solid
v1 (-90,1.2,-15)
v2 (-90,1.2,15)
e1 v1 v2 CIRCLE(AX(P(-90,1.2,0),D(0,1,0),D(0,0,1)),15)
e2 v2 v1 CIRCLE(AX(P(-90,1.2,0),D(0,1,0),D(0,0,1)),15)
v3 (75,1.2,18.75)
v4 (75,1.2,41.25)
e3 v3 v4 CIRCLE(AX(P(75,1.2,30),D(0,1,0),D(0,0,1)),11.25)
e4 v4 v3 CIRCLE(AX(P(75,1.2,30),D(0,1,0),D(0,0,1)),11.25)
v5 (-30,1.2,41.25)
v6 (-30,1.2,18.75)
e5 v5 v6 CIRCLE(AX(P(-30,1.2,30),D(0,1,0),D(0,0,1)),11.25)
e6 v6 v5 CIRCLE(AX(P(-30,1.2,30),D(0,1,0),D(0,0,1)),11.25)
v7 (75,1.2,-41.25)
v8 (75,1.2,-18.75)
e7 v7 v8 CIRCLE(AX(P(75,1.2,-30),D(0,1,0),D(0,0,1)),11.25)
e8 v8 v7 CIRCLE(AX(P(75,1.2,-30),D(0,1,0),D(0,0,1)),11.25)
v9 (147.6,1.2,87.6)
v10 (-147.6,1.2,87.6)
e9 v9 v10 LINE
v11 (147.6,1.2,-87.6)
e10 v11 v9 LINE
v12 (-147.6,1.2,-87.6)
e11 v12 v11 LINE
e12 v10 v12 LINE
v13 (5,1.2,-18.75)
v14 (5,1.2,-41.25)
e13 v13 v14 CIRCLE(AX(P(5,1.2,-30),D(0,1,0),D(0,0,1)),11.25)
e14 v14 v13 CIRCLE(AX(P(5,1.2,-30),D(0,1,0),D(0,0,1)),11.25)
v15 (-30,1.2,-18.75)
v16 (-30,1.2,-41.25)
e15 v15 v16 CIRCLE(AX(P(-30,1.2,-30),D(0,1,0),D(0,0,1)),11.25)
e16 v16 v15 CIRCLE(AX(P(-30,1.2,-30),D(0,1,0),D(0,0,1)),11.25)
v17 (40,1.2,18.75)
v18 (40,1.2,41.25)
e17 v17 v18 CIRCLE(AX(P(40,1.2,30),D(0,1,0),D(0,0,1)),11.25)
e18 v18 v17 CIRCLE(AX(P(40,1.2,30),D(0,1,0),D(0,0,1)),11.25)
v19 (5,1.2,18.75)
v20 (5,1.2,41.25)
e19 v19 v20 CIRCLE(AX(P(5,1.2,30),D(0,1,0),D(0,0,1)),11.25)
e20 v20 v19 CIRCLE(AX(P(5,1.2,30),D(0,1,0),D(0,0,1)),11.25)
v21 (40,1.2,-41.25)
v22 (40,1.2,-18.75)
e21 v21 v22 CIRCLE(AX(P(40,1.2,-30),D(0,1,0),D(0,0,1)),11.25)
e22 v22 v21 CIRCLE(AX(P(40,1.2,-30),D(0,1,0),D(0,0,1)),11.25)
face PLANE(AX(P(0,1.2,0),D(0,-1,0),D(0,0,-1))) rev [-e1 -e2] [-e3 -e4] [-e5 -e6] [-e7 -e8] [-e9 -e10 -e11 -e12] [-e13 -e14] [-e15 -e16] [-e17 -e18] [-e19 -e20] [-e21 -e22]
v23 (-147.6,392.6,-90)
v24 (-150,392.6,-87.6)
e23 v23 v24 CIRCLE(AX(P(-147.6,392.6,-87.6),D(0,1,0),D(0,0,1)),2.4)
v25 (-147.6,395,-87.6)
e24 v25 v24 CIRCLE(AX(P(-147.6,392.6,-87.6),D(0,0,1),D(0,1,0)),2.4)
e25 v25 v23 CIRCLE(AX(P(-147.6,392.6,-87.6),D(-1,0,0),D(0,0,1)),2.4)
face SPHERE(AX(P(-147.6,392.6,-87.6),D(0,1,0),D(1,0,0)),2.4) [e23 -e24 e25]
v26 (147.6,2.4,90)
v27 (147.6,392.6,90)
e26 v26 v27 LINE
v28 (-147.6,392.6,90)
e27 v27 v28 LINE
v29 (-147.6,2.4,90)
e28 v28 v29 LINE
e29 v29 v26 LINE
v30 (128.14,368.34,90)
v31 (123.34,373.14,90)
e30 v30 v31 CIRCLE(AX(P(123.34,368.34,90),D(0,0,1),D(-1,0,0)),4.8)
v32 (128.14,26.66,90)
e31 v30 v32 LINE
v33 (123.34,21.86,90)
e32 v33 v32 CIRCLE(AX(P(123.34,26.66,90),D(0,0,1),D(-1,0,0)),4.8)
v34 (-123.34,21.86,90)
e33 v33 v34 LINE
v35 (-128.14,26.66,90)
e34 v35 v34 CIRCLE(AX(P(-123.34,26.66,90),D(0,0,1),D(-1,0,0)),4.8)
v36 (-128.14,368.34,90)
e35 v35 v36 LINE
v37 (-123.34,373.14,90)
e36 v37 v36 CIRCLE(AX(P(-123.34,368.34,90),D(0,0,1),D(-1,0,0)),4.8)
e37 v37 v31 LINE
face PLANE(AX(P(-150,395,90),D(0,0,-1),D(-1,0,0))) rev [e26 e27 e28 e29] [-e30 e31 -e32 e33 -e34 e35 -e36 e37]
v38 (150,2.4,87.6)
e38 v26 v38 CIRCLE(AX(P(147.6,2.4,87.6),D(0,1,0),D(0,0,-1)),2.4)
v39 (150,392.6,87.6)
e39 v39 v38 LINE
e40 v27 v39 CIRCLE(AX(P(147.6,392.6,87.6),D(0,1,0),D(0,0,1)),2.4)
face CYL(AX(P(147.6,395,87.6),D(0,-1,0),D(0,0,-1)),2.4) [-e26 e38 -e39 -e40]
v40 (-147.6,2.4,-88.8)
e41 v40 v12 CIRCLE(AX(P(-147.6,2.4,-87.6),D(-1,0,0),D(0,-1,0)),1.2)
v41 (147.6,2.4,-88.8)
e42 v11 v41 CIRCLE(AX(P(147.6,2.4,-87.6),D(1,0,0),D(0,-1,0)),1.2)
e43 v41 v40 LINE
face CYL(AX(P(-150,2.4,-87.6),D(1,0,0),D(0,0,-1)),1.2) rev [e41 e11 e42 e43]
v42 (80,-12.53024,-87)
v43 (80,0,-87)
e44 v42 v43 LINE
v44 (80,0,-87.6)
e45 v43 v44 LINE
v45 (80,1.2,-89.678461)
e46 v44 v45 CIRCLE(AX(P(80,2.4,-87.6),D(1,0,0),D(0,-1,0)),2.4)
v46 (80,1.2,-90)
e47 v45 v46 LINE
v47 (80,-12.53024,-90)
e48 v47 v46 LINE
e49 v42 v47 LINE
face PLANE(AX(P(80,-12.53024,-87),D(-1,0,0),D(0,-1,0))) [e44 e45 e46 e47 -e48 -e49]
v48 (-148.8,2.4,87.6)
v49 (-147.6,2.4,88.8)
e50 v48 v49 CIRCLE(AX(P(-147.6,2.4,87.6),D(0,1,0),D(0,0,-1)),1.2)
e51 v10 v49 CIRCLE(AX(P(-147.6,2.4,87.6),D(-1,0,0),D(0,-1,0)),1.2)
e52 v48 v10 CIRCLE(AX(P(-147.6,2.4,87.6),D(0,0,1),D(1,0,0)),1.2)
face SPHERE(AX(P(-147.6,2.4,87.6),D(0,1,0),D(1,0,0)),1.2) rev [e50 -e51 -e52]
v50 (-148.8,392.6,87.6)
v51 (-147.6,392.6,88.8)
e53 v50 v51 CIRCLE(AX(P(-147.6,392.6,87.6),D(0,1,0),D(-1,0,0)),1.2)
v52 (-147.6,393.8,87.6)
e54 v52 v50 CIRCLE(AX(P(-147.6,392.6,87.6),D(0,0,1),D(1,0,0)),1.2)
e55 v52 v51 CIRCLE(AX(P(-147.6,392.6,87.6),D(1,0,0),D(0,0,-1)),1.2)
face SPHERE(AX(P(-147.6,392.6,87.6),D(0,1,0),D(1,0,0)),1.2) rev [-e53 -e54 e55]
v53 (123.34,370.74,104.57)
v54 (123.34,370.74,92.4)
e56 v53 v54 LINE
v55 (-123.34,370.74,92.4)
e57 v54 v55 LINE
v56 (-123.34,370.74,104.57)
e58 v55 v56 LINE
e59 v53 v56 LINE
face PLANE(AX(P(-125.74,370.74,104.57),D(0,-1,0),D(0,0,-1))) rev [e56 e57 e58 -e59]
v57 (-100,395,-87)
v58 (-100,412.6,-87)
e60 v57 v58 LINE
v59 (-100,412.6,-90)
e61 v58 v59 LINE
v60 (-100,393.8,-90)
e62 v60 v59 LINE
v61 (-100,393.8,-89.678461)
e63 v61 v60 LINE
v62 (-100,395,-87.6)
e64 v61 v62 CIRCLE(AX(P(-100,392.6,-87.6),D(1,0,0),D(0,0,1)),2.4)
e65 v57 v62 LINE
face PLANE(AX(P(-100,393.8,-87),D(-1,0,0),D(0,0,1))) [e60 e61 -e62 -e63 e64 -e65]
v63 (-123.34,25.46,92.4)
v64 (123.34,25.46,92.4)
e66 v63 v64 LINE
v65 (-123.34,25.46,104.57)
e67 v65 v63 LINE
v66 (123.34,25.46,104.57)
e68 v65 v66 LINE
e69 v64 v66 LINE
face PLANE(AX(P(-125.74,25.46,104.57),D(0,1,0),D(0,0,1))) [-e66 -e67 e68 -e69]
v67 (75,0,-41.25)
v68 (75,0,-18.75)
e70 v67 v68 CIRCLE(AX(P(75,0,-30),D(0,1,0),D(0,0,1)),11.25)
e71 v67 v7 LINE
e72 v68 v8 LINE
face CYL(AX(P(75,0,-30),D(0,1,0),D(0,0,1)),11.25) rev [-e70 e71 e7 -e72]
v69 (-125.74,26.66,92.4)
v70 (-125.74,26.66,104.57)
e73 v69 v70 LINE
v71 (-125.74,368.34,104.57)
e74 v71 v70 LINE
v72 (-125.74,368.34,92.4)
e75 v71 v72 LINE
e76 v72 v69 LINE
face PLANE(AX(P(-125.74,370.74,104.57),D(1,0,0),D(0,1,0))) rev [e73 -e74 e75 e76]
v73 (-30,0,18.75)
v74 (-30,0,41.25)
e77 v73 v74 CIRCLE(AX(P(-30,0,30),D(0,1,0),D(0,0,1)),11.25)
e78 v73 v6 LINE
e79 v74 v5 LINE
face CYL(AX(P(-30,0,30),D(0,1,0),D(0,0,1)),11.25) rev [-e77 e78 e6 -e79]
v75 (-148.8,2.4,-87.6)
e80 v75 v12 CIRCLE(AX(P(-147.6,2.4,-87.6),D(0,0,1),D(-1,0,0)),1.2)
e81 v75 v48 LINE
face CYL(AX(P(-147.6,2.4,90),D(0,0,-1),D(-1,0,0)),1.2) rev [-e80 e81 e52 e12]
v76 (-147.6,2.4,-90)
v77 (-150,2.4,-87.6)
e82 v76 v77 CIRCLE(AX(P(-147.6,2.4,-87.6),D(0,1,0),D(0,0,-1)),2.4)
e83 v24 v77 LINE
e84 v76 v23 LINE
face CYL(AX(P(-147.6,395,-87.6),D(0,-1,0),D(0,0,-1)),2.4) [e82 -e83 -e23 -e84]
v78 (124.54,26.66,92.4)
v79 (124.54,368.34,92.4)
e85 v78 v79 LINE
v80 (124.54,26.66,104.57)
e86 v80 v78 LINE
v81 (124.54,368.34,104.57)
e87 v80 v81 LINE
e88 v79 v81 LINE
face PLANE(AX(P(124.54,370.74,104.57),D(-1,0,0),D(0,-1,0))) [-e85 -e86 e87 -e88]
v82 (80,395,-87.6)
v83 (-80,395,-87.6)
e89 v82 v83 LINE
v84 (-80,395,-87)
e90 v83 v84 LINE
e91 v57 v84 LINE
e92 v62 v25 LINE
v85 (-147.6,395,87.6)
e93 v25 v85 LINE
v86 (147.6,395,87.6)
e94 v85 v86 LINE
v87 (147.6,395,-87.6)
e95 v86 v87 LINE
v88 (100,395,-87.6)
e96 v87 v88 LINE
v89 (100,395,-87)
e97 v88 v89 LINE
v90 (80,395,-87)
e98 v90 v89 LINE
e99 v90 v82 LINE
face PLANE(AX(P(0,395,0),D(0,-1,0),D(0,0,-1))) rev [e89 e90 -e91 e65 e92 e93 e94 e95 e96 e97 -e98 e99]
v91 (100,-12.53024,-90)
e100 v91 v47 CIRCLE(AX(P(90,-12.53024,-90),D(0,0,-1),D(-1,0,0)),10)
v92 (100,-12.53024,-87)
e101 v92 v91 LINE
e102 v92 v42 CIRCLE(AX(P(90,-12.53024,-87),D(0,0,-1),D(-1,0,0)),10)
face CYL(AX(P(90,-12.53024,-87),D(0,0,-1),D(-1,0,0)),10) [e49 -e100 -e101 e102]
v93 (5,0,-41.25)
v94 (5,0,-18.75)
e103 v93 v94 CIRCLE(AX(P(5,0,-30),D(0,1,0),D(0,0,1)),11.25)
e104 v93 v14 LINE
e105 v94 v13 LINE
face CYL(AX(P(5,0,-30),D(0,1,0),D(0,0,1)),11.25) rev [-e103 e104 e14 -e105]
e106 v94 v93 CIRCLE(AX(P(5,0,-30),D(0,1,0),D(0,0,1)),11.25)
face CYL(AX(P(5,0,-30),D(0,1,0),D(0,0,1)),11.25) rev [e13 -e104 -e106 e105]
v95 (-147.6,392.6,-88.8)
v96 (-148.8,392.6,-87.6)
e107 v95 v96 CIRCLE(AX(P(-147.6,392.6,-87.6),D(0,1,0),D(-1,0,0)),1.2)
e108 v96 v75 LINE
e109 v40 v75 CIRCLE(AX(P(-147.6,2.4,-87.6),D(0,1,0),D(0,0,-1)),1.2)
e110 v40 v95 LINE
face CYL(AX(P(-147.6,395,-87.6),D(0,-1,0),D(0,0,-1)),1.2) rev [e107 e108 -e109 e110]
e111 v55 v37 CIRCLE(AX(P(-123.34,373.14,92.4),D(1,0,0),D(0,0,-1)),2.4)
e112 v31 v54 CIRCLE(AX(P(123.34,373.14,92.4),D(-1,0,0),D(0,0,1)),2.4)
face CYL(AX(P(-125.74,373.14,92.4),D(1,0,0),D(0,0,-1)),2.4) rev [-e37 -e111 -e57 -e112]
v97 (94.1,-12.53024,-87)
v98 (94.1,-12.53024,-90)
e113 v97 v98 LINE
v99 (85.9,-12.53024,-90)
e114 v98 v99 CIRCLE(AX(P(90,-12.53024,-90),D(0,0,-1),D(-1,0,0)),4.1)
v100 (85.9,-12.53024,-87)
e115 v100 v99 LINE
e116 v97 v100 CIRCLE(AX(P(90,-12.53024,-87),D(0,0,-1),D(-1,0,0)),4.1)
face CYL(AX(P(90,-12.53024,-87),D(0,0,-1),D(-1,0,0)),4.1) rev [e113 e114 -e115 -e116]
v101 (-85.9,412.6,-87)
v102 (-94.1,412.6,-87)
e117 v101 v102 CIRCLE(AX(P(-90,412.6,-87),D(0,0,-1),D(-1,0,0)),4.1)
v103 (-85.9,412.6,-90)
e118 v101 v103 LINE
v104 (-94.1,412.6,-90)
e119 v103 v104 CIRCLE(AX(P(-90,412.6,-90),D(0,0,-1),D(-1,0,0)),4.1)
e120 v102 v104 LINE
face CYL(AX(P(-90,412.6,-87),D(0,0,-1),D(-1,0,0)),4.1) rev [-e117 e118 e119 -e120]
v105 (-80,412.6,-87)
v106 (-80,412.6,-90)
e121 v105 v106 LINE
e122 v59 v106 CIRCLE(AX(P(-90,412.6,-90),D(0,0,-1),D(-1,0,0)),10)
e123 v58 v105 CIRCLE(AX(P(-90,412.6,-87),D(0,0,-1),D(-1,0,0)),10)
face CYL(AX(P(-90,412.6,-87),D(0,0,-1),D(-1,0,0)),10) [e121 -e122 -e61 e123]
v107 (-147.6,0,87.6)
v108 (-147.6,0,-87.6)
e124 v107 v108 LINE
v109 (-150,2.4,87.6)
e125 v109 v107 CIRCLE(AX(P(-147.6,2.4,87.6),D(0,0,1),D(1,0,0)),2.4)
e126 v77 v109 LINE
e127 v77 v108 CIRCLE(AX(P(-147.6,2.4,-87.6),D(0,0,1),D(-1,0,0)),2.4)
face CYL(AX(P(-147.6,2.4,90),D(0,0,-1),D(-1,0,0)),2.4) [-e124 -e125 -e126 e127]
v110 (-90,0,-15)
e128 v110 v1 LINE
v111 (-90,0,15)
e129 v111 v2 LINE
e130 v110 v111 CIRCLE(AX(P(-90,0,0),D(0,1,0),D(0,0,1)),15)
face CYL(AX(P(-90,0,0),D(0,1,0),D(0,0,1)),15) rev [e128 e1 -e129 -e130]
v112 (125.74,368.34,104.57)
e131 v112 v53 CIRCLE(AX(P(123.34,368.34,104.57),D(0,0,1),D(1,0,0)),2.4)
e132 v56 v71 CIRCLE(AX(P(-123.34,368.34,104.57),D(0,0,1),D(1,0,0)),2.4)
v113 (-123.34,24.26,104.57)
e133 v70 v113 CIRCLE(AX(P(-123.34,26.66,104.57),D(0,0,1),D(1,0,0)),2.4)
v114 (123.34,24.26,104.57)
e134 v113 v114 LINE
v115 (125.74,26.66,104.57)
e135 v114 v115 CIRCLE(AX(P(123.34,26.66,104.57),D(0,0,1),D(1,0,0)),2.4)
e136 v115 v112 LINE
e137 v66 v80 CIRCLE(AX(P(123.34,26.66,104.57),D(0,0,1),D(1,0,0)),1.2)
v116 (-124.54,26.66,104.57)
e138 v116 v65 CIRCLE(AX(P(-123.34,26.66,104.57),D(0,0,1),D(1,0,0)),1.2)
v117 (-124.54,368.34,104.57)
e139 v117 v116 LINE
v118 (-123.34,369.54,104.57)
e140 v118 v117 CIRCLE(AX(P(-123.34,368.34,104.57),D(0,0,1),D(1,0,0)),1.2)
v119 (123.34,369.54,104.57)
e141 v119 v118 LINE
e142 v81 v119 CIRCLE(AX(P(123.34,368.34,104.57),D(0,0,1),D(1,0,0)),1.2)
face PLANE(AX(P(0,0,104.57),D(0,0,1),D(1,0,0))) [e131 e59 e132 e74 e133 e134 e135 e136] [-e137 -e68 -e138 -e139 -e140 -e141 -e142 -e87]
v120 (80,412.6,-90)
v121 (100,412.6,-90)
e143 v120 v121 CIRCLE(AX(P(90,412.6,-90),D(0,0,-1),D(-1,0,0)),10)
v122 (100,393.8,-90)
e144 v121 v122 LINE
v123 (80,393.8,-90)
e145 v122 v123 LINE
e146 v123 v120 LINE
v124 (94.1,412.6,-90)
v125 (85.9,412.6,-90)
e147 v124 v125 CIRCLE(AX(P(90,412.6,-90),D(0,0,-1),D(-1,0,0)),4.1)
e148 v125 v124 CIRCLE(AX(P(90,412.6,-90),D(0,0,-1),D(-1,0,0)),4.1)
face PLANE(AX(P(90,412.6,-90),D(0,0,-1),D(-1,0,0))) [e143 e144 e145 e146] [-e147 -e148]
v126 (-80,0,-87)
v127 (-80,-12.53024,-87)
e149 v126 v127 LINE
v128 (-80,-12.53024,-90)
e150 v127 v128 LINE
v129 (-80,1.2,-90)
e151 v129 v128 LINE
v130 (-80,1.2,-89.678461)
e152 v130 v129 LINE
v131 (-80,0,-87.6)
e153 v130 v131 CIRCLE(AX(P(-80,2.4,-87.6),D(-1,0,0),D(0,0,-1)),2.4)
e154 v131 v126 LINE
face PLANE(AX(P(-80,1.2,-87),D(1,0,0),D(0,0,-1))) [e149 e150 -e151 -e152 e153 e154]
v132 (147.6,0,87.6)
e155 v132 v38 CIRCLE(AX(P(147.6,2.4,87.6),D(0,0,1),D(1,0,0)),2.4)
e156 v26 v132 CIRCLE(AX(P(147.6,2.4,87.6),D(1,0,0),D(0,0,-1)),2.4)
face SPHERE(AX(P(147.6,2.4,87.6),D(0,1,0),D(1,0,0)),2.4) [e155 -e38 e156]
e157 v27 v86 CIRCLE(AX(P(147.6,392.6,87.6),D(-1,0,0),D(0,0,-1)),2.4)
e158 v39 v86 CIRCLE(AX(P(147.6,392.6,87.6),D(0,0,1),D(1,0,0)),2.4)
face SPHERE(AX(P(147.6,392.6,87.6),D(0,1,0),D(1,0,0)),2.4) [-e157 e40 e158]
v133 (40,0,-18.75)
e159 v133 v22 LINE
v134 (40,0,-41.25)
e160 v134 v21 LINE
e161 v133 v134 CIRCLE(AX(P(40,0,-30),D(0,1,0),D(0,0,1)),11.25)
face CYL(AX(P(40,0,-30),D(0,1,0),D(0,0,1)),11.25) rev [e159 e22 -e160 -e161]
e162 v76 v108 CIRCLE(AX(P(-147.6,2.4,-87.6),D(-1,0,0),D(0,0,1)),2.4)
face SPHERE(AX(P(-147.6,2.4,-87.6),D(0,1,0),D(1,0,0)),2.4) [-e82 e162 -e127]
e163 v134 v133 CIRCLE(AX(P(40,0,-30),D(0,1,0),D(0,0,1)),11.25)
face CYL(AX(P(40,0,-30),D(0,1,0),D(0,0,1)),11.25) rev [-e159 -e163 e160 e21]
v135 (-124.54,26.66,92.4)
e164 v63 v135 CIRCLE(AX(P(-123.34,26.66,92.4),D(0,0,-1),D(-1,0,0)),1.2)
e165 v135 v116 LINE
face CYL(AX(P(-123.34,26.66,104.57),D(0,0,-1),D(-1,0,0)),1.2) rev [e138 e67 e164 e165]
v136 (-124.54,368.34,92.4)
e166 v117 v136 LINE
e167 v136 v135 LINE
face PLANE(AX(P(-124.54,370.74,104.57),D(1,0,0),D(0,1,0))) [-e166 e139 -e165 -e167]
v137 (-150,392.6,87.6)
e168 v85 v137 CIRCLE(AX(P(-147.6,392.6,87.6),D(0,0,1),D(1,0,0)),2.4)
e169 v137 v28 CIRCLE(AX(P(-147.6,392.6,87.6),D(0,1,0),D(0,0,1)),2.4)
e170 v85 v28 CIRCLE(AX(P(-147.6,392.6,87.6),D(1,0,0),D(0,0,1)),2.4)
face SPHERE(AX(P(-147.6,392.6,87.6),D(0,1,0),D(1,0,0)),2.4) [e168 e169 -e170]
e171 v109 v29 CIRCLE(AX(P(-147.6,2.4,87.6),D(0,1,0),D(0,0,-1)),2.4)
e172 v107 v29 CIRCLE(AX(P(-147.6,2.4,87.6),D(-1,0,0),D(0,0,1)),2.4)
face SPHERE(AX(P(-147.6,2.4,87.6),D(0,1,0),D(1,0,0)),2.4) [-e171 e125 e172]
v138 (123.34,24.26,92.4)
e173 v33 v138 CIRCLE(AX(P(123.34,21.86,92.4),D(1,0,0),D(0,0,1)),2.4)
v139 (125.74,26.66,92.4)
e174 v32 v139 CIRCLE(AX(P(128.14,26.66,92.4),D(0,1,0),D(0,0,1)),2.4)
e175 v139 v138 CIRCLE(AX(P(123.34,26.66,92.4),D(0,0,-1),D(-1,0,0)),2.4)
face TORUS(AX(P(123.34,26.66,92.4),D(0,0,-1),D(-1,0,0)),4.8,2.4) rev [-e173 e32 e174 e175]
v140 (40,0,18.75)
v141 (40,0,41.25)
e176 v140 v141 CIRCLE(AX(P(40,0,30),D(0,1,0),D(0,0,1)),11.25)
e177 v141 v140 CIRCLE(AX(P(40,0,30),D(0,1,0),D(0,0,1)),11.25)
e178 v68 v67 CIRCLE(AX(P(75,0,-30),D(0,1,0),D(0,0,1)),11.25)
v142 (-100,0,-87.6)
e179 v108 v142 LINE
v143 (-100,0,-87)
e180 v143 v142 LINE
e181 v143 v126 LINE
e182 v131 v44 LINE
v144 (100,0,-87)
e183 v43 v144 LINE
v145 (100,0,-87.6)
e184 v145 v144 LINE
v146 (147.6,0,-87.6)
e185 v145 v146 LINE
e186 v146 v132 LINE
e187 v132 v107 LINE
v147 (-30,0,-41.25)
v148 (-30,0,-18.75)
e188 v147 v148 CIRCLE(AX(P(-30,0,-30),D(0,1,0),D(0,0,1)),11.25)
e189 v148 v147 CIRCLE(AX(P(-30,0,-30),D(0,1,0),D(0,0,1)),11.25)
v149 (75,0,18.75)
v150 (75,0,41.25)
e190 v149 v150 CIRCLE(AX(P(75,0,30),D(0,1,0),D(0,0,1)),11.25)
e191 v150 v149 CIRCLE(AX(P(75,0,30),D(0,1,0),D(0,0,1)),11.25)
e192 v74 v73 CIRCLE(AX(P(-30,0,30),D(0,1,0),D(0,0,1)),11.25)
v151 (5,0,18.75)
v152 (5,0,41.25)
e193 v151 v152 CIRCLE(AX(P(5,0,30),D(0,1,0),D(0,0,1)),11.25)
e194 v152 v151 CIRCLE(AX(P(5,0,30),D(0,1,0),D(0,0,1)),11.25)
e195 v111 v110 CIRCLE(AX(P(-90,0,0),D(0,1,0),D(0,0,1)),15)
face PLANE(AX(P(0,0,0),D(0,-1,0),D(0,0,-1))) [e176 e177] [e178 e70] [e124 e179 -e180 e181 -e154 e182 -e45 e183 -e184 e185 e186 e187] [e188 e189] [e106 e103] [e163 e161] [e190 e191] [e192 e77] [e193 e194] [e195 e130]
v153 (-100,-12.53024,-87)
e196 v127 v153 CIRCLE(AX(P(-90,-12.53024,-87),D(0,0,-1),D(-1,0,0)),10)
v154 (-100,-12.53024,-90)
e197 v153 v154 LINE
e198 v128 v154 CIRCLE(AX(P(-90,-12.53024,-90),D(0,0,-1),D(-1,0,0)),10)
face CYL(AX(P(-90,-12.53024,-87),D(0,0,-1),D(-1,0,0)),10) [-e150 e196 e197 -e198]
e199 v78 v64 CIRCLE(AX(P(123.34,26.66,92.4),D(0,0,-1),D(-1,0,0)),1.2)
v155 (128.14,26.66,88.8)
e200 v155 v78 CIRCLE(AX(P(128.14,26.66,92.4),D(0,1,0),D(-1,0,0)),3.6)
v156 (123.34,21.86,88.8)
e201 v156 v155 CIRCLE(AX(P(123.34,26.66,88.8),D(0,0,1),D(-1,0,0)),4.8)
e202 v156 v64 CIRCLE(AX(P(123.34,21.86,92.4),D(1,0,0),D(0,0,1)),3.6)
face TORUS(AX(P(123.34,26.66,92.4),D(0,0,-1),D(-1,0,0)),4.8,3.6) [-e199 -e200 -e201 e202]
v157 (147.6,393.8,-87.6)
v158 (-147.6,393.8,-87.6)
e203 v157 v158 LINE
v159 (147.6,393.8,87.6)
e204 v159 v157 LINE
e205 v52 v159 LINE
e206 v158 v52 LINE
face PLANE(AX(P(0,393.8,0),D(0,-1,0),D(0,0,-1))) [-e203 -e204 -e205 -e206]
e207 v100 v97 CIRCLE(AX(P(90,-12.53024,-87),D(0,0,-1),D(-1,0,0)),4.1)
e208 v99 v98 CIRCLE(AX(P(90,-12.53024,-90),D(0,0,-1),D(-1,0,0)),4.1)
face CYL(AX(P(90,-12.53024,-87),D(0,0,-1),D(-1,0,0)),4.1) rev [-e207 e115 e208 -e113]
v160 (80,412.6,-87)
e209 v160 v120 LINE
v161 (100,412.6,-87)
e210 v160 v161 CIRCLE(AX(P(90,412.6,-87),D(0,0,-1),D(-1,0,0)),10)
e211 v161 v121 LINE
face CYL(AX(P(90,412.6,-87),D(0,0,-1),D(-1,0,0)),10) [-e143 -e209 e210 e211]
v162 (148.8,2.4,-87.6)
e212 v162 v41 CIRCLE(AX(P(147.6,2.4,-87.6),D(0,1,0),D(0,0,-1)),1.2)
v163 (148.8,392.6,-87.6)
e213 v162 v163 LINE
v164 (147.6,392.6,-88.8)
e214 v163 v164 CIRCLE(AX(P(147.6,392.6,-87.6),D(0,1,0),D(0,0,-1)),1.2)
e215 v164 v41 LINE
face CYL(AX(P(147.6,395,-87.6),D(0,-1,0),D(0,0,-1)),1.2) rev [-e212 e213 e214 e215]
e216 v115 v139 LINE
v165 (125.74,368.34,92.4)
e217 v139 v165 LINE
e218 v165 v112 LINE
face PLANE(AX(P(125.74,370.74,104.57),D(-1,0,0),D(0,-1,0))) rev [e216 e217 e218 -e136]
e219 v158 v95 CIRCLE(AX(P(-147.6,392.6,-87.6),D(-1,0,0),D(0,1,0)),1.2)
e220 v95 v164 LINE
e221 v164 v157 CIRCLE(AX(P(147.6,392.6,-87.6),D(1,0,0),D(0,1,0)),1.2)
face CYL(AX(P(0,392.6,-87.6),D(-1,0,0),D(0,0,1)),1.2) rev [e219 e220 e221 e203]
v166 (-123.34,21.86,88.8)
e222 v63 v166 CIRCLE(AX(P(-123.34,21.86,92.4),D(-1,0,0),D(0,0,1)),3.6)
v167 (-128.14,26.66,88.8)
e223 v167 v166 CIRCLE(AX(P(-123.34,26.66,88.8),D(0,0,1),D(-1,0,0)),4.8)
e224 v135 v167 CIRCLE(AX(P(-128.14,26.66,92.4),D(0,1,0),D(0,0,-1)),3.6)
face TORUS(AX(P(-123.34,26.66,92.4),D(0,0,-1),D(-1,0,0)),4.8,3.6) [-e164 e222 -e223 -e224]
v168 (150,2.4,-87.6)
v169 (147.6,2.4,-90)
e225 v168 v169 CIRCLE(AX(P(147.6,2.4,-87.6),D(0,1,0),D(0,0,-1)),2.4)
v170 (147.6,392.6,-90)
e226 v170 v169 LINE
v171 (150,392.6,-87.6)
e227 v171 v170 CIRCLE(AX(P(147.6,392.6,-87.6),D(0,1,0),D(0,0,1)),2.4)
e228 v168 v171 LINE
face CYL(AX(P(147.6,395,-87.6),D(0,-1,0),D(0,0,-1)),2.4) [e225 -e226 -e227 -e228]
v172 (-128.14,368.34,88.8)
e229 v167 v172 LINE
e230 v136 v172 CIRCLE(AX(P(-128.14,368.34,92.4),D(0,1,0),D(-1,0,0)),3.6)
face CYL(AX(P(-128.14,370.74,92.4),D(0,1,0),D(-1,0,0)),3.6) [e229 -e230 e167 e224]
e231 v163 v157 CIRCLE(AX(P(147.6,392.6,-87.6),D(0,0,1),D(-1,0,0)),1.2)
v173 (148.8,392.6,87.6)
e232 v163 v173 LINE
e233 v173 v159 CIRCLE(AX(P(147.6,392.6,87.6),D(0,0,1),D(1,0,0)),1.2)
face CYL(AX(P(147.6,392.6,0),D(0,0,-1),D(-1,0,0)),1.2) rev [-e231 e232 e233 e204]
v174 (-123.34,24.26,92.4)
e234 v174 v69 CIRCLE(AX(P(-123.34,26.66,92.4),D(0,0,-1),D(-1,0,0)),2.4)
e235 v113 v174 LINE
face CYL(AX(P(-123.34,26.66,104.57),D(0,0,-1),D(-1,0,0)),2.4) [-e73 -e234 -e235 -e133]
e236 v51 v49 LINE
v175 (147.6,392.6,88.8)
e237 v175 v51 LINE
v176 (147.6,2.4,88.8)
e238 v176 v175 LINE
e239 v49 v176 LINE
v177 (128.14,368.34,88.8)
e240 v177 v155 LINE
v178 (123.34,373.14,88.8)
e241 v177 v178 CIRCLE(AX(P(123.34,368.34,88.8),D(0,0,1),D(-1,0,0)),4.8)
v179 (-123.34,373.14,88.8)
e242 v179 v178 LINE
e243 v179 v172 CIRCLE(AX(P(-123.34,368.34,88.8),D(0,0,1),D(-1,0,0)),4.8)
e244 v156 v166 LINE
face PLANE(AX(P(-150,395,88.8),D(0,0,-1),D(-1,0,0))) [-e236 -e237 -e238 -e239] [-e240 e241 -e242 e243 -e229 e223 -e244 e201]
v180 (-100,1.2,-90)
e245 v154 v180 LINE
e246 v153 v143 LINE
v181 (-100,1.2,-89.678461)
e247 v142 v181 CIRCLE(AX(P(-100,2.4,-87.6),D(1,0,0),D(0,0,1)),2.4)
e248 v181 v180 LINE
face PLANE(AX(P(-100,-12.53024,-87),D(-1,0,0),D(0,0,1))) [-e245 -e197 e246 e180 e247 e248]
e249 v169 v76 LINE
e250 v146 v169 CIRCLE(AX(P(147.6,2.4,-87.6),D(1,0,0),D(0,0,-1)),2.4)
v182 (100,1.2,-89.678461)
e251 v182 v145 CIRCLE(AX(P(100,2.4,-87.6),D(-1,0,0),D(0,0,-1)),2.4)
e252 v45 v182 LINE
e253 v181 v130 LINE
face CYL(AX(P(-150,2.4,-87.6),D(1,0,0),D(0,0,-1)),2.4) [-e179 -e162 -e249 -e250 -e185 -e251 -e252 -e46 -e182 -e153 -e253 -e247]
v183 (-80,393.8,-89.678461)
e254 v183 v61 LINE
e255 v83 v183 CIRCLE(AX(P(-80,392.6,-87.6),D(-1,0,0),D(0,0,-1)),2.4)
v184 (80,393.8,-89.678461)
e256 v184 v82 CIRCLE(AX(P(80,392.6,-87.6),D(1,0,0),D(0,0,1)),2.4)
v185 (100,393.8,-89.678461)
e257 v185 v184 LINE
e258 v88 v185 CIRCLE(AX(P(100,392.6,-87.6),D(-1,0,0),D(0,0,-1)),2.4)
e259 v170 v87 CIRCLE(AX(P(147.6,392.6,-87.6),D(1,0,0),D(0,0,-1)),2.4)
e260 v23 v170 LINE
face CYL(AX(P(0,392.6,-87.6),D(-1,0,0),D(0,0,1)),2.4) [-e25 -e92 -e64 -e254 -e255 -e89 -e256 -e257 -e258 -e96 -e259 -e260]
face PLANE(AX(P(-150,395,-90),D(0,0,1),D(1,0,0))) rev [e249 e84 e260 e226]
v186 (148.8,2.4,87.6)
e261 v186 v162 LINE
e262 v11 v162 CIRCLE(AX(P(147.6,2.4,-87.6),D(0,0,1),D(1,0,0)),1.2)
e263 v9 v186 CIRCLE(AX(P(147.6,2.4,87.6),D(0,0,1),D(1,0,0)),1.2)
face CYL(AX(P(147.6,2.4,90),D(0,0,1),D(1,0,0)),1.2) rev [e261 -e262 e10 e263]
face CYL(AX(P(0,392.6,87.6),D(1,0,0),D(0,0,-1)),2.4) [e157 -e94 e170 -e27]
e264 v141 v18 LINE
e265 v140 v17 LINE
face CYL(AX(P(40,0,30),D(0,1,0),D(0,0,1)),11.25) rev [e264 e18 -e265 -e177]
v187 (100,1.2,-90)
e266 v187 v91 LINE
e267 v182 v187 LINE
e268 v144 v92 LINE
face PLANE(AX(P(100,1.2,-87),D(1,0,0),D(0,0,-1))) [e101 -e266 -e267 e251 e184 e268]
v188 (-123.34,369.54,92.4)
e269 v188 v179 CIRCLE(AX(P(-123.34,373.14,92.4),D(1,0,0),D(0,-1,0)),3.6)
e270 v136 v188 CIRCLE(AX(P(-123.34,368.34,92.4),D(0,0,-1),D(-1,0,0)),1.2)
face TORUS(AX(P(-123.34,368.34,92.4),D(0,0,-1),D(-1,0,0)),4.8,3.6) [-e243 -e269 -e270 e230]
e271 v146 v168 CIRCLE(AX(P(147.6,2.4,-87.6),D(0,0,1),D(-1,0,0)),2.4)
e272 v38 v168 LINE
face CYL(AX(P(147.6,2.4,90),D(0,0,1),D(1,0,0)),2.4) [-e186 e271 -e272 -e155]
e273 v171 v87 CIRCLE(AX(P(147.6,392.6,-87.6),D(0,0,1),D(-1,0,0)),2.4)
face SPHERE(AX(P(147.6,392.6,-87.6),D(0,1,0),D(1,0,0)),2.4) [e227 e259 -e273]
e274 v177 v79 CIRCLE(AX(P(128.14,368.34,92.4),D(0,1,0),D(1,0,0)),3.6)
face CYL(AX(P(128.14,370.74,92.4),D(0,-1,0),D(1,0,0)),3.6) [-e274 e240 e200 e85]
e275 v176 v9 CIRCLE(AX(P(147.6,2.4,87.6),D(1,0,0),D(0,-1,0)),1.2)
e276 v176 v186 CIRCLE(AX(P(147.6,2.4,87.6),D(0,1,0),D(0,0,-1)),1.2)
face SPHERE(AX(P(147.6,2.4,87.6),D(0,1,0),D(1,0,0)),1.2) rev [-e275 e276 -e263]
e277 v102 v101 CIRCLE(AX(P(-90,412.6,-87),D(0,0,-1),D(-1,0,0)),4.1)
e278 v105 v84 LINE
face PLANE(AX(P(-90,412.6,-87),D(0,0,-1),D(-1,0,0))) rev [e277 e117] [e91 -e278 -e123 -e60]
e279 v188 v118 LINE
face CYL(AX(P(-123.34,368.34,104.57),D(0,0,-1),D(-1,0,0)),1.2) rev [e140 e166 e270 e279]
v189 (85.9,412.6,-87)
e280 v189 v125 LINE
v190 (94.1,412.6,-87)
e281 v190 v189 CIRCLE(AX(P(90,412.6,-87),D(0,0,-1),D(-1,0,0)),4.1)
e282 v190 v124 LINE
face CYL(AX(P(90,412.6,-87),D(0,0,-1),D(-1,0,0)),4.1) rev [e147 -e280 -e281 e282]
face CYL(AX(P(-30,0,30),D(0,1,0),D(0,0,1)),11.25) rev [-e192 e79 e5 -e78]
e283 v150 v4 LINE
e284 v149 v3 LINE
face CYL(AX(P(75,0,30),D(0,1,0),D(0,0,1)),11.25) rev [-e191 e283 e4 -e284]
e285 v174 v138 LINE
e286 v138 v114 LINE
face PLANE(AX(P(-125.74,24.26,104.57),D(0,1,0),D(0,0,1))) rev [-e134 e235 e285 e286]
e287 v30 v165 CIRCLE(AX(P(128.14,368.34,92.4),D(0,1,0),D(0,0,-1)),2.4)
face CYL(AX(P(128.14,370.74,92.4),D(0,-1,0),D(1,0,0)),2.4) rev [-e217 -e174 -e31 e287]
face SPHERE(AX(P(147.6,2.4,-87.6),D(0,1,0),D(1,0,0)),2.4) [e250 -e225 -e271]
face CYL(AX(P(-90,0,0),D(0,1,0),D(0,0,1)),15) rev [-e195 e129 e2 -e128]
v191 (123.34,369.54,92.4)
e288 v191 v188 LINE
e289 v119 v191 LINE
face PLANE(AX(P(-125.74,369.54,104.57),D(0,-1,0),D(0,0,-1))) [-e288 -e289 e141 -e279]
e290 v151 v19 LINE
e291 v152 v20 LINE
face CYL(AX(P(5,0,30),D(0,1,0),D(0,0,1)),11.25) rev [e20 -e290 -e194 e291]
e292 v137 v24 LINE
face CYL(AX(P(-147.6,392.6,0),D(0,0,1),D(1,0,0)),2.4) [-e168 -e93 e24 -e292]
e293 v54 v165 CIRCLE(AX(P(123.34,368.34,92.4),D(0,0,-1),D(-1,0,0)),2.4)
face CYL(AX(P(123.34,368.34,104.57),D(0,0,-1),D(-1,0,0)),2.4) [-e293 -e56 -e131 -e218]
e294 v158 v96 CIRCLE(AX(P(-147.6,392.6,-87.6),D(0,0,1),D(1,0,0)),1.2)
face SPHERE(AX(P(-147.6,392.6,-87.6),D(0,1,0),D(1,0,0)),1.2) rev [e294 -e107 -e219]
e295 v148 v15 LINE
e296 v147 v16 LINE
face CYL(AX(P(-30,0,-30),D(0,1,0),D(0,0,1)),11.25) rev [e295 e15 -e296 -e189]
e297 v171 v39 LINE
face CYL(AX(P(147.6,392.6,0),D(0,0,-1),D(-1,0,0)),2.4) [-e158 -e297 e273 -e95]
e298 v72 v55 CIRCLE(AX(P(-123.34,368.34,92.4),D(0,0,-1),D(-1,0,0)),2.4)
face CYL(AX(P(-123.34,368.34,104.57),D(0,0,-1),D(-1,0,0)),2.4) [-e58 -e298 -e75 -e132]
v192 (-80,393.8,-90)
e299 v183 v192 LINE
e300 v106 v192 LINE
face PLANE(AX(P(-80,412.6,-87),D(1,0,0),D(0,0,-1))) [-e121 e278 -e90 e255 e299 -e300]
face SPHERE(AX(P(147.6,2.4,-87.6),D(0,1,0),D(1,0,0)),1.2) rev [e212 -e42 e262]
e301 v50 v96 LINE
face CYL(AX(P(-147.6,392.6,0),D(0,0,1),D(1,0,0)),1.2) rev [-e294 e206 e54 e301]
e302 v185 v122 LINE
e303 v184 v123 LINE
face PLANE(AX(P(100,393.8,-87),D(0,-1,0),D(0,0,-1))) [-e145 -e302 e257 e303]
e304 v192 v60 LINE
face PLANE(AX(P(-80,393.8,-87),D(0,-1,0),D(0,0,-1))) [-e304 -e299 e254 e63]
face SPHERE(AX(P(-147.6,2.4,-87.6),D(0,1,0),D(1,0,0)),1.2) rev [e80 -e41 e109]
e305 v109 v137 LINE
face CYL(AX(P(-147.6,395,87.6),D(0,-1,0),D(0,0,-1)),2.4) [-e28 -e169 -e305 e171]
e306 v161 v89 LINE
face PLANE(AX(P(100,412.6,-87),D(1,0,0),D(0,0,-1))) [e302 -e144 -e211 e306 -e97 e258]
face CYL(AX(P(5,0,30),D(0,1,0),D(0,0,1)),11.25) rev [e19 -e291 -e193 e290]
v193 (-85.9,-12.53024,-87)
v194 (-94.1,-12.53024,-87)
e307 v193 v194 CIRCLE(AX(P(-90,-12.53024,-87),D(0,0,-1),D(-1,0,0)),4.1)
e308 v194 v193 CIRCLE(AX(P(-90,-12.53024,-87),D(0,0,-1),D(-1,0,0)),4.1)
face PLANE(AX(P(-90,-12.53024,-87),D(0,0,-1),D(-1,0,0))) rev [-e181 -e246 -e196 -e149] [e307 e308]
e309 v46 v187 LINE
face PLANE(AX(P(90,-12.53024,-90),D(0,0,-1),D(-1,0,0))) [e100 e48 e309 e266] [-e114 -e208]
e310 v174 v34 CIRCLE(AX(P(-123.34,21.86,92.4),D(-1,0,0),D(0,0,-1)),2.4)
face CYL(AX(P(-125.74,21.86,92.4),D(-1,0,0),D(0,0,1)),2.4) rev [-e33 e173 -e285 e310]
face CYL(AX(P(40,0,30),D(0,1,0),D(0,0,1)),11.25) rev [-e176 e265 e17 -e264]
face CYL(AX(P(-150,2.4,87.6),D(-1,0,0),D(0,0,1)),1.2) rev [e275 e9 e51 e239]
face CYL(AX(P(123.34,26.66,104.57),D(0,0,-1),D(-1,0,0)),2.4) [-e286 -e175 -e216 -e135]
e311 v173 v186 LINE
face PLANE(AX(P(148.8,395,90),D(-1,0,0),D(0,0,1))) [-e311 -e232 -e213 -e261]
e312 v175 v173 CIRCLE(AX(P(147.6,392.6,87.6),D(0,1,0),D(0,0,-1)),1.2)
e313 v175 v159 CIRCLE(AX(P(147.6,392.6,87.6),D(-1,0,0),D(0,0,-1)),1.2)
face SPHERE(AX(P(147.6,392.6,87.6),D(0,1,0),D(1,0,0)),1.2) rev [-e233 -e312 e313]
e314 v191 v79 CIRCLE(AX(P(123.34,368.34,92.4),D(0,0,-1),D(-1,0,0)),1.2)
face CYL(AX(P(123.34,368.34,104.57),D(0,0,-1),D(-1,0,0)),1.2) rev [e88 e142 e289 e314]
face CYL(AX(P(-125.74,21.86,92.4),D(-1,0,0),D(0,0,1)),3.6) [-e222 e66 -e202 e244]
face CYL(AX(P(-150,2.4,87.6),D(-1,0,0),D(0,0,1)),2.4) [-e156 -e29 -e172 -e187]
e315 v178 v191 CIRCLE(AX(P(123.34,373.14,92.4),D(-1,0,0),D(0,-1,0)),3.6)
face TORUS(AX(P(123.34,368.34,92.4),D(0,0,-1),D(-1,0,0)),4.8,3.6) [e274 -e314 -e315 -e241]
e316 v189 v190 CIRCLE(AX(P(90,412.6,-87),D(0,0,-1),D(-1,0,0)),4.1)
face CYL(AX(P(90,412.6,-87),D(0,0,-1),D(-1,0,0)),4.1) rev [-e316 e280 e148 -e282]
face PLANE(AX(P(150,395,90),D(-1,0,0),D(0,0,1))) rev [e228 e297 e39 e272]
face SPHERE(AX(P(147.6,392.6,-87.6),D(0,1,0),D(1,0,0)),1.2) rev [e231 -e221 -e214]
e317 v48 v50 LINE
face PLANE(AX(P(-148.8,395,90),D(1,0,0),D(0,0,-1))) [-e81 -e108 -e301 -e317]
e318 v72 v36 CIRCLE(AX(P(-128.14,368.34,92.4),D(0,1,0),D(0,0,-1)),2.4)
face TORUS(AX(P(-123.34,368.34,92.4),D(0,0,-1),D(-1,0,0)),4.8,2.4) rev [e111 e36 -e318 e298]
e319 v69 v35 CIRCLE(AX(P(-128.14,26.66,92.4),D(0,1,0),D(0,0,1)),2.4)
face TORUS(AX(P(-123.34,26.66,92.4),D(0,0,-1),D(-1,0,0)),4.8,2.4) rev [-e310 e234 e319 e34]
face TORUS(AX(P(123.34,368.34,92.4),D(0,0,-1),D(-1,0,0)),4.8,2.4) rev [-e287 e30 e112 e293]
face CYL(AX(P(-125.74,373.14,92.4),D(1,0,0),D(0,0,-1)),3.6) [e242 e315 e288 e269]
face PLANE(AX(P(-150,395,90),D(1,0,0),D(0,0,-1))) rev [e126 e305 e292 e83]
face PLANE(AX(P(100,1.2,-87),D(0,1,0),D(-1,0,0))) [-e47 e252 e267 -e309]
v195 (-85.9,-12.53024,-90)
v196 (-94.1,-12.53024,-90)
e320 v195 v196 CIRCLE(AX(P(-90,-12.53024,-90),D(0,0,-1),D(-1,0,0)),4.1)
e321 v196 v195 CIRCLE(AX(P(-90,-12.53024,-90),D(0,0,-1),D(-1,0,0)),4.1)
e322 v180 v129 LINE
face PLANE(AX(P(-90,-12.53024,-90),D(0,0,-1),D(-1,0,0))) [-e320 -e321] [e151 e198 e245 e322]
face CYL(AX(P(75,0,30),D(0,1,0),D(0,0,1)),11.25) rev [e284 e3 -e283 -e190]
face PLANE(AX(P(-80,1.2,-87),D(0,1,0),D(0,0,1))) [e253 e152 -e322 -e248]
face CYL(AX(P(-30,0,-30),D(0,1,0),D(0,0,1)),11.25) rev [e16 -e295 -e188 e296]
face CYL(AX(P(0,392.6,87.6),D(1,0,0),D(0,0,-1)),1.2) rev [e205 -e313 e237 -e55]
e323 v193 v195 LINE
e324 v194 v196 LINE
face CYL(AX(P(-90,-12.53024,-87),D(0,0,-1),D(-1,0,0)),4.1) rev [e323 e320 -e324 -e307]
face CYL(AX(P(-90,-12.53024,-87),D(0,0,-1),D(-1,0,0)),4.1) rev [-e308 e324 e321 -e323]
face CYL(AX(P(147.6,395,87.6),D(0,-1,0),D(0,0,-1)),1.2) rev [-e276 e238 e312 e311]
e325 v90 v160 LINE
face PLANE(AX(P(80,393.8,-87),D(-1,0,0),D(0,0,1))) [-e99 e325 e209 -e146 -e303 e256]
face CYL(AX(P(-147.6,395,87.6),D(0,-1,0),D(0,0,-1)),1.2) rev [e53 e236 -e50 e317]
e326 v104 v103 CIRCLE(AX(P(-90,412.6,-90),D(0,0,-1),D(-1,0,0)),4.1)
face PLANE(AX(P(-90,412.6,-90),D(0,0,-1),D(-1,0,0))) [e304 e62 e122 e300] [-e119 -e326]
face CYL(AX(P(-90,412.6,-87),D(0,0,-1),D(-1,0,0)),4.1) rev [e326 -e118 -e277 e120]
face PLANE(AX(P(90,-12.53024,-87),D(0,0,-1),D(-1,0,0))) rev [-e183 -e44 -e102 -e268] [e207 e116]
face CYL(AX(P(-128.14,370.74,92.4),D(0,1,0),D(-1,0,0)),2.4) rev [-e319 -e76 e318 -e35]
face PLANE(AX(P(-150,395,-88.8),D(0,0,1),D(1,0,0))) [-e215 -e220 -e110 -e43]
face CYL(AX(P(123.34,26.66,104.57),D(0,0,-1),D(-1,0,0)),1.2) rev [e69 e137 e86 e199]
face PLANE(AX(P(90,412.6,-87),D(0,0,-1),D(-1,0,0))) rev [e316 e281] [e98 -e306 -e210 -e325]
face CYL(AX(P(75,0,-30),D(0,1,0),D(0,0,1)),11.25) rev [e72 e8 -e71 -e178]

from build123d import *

# Parameters (mm, degrees)
SKETCH1_W           = 300
SKETCH1_H           = 180
BOSS_EXTRUDE1_DEPTH = 395
FILLET1_R           = 2.4
SKETCH2_W           = 251.48
SKETCH2_H           = 346.48
BOSS_EXTRUDE2_DEPTH = 14.57
FILLET2_R           = 2.4
SHELL1_T            = -1.2
SKETCH3_R           = 15
SKETCH3_R_2         = 11.25
CUT_EXTRUDE1_DEPTH  = 435.181212053
SKETCH4_R           = 4.1
BOSS_EXTRUDE3_DEPTH = 3


with BuildPart() as part:
    # Sketch1 → Boss-Extrude1 (new body)
    with BuildSketch(Plane(origin=(0, 0, 0), x_dir=(1, 0, 0), z_dir=(0, 1, 0))):
        Rectangle(SKETCH1_W, SKETCH1_H)
    extrude(amount=BOSS_EXTRUDE1_DEPTH)

    # Fillet1
    fillet1_edges = [part.edges().sort_by_distance(p)[0] for p in [
        (-150, 395, 0),
        (0, 395, 90),
        (150, 395, 0),
        (0, 0, 90),
        (-150, 0, 0),
        (0, 0, -90),
        (150, 0, 0),
        (0, 395, -90),
        (150, 197.5, 90),
        (-150, 197.5, 90),
        (-150, 197.5, -90),
        (150, 197.5, -90),
    ]]
    fillet(fillet1_edges, radius=FILLET1_R)

    # Sketch2 → Boss-Extrude2 (add)
    with BuildSketch(Plane.XY.offset(90)):
        with Locations((0, 197.5)):
            Rectangle(SKETCH2_W, SKETCH2_H)
    extrude(amount=BOSS_EXTRUDE2_DEPTH)

    # Fillet2
    fillet2_edges = [part.edges().sort_by_distance(p)[0] for p in [
        (-125.74, 197.5, 90),
        (-125.74, 370.74, 97.285),
        (0, 24.26, 90),
        (-125.74, 24.26, 97.285),
        (125.74, 197.5, 90),
        (125.74, 24.26, 97.285),
        (0, 370.74, 90),
        (125.74, 370.74, 97.285),
    ]]
    fillet(fillet2_edges, radius=FILLET2_R)

    # Shell1
    shell1_openings = [part.faces().sort_by_distance(p)[0] for p in [
        (0, 197.5, 104.57),
    ]]
    offset(amount=SHELL1_T, openings=shell1_openings, kind=Kind.INTERSECTION)

    # Sketch3 → Cut-Extrude1 (cut, through all)
    with BuildSketch(Plane(origin=(0, 1.2, 0), x_dir=(1, 0, 0), z_dir=(0, 1, 0))):
        with Locations(Location((-90, 0, 0), (0, 0, 270))):
            Circle(SKETCH3_R)
        with Locations(Location((-30, -30, 0), (0, 0, 270))):
            Circle(SKETCH3_R_2)
        with Locations(Location((-30, 30, 0), (0, 0, 270))):
            Circle(SKETCH3_R_2)
        with Locations(Location((5, -30, 0), (0, 0, 270))):
            Circle(SKETCH3_R_2)
        with Locations(Location((5, 30, 0), (0, 0, 270))):
            Circle(SKETCH3_R_2)
        with Locations(Location((40, -30, 0), (0, 0, 270))):
            Circle(SKETCH3_R_2)
        with Locations(Location((40, 30, 0), (0, 0, 270))):
            Circle(SKETCH3_R_2)
        with Locations(Location((75, -30, 0), (0, 0, 270))):
            Circle(SKETCH3_R_2)
        with Locations(Location((75, 30, 0), (0, 0, 270))):
            Circle(SKETCH3_R_2)
    extrude(amount=-CUT_EXTRUDE1_DEPTH, mode=Mode.SUBTRACT)

    # Sketch4 → Boss-Extrude3 (add)
    # profile 1 of 4: a face of its own
    with BuildSketch(Plane(origin=(0, 0, -90), x_dir=(-1, 0, 0), z_dir=(0, 0, -1))):
        with BuildLine():
            Line((-100, 412.6), (-100, 393.8))
            Line((-100, 393.8), (-80, 393.8))
            Line((-80, 393.8), (-80, 412.6))
            ThreePointArc((-80, 412.6), (-90, 422.6), (-100, 412.6))
        make_face()
        with Locations((-90, 412.6)):
            Circle(SKETCH4_R, mode=Mode.SUBTRACT)
    # profile 2 of 4: a face of its own
    with BuildSketch(Plane(origin=(0, 0, -90), x_dir=(-1, 0, 0), z_dir=(0, 0, -1))):
        with BuildLine():
            Line((80, 412.6), (80, 393.8))
            Line((80, 393.8), (100, 393.8))
            Line((100, 393.8), (100, 412.6))
            ThreePointArc((100, 412.6), (90, 422.6), (80, 412.6))
        make_face()
        with Locations((90, 412.6)):
            Circle(SKETCH4_R, mode=Mode.SUBTRACT)
    # profile 3 of 4: a face of its own
    with BuildSketch(Plane(origin=(0, 0, -90), x_dir=(-1, 0, 0), z_dir=(0, 0, -1))):
        with BuildLine():
            Line((-100, 1.2), (-100, -12.530239685))
            ThreePointArc((-100, -12.530239685), (-90, -22.530239685), (-80, -12.530239685))
            Line((-80, -12.530239685), (-80, 1.2))
            Line((-80, 1.2), (-100, 1.2))
        make_face()
        with Locations((-90, -12.530239685)):
            Circle(SKETCH4_R, mode=Mode.SUBTRACT)
    # profile 4 of 4: a face of its own
    with BuildSketch(Plane(origin=(0, 0, -90), x_dir=(-1, 0, 0), z_dir=(0, 0, -1))):
        with BuildLine():
            Line((80, 1.2), (80, -12.530239685))
            ThreePointArc((80, -12.530239685), (90, -22.530239685), (100, -12.530239685))
            Line((100, -12.530239685), (100, 1.2))
            Line((100, 1.2), (80, 1.2))
        make_face()
        with Locations((90, -12.530239685)):
            Circle(SKETCH4_R, mode=Mode.SUBTRACT)
    extrude(amount=-BOSS_EXTRUDE3_DEPTH)


solid = part.part
